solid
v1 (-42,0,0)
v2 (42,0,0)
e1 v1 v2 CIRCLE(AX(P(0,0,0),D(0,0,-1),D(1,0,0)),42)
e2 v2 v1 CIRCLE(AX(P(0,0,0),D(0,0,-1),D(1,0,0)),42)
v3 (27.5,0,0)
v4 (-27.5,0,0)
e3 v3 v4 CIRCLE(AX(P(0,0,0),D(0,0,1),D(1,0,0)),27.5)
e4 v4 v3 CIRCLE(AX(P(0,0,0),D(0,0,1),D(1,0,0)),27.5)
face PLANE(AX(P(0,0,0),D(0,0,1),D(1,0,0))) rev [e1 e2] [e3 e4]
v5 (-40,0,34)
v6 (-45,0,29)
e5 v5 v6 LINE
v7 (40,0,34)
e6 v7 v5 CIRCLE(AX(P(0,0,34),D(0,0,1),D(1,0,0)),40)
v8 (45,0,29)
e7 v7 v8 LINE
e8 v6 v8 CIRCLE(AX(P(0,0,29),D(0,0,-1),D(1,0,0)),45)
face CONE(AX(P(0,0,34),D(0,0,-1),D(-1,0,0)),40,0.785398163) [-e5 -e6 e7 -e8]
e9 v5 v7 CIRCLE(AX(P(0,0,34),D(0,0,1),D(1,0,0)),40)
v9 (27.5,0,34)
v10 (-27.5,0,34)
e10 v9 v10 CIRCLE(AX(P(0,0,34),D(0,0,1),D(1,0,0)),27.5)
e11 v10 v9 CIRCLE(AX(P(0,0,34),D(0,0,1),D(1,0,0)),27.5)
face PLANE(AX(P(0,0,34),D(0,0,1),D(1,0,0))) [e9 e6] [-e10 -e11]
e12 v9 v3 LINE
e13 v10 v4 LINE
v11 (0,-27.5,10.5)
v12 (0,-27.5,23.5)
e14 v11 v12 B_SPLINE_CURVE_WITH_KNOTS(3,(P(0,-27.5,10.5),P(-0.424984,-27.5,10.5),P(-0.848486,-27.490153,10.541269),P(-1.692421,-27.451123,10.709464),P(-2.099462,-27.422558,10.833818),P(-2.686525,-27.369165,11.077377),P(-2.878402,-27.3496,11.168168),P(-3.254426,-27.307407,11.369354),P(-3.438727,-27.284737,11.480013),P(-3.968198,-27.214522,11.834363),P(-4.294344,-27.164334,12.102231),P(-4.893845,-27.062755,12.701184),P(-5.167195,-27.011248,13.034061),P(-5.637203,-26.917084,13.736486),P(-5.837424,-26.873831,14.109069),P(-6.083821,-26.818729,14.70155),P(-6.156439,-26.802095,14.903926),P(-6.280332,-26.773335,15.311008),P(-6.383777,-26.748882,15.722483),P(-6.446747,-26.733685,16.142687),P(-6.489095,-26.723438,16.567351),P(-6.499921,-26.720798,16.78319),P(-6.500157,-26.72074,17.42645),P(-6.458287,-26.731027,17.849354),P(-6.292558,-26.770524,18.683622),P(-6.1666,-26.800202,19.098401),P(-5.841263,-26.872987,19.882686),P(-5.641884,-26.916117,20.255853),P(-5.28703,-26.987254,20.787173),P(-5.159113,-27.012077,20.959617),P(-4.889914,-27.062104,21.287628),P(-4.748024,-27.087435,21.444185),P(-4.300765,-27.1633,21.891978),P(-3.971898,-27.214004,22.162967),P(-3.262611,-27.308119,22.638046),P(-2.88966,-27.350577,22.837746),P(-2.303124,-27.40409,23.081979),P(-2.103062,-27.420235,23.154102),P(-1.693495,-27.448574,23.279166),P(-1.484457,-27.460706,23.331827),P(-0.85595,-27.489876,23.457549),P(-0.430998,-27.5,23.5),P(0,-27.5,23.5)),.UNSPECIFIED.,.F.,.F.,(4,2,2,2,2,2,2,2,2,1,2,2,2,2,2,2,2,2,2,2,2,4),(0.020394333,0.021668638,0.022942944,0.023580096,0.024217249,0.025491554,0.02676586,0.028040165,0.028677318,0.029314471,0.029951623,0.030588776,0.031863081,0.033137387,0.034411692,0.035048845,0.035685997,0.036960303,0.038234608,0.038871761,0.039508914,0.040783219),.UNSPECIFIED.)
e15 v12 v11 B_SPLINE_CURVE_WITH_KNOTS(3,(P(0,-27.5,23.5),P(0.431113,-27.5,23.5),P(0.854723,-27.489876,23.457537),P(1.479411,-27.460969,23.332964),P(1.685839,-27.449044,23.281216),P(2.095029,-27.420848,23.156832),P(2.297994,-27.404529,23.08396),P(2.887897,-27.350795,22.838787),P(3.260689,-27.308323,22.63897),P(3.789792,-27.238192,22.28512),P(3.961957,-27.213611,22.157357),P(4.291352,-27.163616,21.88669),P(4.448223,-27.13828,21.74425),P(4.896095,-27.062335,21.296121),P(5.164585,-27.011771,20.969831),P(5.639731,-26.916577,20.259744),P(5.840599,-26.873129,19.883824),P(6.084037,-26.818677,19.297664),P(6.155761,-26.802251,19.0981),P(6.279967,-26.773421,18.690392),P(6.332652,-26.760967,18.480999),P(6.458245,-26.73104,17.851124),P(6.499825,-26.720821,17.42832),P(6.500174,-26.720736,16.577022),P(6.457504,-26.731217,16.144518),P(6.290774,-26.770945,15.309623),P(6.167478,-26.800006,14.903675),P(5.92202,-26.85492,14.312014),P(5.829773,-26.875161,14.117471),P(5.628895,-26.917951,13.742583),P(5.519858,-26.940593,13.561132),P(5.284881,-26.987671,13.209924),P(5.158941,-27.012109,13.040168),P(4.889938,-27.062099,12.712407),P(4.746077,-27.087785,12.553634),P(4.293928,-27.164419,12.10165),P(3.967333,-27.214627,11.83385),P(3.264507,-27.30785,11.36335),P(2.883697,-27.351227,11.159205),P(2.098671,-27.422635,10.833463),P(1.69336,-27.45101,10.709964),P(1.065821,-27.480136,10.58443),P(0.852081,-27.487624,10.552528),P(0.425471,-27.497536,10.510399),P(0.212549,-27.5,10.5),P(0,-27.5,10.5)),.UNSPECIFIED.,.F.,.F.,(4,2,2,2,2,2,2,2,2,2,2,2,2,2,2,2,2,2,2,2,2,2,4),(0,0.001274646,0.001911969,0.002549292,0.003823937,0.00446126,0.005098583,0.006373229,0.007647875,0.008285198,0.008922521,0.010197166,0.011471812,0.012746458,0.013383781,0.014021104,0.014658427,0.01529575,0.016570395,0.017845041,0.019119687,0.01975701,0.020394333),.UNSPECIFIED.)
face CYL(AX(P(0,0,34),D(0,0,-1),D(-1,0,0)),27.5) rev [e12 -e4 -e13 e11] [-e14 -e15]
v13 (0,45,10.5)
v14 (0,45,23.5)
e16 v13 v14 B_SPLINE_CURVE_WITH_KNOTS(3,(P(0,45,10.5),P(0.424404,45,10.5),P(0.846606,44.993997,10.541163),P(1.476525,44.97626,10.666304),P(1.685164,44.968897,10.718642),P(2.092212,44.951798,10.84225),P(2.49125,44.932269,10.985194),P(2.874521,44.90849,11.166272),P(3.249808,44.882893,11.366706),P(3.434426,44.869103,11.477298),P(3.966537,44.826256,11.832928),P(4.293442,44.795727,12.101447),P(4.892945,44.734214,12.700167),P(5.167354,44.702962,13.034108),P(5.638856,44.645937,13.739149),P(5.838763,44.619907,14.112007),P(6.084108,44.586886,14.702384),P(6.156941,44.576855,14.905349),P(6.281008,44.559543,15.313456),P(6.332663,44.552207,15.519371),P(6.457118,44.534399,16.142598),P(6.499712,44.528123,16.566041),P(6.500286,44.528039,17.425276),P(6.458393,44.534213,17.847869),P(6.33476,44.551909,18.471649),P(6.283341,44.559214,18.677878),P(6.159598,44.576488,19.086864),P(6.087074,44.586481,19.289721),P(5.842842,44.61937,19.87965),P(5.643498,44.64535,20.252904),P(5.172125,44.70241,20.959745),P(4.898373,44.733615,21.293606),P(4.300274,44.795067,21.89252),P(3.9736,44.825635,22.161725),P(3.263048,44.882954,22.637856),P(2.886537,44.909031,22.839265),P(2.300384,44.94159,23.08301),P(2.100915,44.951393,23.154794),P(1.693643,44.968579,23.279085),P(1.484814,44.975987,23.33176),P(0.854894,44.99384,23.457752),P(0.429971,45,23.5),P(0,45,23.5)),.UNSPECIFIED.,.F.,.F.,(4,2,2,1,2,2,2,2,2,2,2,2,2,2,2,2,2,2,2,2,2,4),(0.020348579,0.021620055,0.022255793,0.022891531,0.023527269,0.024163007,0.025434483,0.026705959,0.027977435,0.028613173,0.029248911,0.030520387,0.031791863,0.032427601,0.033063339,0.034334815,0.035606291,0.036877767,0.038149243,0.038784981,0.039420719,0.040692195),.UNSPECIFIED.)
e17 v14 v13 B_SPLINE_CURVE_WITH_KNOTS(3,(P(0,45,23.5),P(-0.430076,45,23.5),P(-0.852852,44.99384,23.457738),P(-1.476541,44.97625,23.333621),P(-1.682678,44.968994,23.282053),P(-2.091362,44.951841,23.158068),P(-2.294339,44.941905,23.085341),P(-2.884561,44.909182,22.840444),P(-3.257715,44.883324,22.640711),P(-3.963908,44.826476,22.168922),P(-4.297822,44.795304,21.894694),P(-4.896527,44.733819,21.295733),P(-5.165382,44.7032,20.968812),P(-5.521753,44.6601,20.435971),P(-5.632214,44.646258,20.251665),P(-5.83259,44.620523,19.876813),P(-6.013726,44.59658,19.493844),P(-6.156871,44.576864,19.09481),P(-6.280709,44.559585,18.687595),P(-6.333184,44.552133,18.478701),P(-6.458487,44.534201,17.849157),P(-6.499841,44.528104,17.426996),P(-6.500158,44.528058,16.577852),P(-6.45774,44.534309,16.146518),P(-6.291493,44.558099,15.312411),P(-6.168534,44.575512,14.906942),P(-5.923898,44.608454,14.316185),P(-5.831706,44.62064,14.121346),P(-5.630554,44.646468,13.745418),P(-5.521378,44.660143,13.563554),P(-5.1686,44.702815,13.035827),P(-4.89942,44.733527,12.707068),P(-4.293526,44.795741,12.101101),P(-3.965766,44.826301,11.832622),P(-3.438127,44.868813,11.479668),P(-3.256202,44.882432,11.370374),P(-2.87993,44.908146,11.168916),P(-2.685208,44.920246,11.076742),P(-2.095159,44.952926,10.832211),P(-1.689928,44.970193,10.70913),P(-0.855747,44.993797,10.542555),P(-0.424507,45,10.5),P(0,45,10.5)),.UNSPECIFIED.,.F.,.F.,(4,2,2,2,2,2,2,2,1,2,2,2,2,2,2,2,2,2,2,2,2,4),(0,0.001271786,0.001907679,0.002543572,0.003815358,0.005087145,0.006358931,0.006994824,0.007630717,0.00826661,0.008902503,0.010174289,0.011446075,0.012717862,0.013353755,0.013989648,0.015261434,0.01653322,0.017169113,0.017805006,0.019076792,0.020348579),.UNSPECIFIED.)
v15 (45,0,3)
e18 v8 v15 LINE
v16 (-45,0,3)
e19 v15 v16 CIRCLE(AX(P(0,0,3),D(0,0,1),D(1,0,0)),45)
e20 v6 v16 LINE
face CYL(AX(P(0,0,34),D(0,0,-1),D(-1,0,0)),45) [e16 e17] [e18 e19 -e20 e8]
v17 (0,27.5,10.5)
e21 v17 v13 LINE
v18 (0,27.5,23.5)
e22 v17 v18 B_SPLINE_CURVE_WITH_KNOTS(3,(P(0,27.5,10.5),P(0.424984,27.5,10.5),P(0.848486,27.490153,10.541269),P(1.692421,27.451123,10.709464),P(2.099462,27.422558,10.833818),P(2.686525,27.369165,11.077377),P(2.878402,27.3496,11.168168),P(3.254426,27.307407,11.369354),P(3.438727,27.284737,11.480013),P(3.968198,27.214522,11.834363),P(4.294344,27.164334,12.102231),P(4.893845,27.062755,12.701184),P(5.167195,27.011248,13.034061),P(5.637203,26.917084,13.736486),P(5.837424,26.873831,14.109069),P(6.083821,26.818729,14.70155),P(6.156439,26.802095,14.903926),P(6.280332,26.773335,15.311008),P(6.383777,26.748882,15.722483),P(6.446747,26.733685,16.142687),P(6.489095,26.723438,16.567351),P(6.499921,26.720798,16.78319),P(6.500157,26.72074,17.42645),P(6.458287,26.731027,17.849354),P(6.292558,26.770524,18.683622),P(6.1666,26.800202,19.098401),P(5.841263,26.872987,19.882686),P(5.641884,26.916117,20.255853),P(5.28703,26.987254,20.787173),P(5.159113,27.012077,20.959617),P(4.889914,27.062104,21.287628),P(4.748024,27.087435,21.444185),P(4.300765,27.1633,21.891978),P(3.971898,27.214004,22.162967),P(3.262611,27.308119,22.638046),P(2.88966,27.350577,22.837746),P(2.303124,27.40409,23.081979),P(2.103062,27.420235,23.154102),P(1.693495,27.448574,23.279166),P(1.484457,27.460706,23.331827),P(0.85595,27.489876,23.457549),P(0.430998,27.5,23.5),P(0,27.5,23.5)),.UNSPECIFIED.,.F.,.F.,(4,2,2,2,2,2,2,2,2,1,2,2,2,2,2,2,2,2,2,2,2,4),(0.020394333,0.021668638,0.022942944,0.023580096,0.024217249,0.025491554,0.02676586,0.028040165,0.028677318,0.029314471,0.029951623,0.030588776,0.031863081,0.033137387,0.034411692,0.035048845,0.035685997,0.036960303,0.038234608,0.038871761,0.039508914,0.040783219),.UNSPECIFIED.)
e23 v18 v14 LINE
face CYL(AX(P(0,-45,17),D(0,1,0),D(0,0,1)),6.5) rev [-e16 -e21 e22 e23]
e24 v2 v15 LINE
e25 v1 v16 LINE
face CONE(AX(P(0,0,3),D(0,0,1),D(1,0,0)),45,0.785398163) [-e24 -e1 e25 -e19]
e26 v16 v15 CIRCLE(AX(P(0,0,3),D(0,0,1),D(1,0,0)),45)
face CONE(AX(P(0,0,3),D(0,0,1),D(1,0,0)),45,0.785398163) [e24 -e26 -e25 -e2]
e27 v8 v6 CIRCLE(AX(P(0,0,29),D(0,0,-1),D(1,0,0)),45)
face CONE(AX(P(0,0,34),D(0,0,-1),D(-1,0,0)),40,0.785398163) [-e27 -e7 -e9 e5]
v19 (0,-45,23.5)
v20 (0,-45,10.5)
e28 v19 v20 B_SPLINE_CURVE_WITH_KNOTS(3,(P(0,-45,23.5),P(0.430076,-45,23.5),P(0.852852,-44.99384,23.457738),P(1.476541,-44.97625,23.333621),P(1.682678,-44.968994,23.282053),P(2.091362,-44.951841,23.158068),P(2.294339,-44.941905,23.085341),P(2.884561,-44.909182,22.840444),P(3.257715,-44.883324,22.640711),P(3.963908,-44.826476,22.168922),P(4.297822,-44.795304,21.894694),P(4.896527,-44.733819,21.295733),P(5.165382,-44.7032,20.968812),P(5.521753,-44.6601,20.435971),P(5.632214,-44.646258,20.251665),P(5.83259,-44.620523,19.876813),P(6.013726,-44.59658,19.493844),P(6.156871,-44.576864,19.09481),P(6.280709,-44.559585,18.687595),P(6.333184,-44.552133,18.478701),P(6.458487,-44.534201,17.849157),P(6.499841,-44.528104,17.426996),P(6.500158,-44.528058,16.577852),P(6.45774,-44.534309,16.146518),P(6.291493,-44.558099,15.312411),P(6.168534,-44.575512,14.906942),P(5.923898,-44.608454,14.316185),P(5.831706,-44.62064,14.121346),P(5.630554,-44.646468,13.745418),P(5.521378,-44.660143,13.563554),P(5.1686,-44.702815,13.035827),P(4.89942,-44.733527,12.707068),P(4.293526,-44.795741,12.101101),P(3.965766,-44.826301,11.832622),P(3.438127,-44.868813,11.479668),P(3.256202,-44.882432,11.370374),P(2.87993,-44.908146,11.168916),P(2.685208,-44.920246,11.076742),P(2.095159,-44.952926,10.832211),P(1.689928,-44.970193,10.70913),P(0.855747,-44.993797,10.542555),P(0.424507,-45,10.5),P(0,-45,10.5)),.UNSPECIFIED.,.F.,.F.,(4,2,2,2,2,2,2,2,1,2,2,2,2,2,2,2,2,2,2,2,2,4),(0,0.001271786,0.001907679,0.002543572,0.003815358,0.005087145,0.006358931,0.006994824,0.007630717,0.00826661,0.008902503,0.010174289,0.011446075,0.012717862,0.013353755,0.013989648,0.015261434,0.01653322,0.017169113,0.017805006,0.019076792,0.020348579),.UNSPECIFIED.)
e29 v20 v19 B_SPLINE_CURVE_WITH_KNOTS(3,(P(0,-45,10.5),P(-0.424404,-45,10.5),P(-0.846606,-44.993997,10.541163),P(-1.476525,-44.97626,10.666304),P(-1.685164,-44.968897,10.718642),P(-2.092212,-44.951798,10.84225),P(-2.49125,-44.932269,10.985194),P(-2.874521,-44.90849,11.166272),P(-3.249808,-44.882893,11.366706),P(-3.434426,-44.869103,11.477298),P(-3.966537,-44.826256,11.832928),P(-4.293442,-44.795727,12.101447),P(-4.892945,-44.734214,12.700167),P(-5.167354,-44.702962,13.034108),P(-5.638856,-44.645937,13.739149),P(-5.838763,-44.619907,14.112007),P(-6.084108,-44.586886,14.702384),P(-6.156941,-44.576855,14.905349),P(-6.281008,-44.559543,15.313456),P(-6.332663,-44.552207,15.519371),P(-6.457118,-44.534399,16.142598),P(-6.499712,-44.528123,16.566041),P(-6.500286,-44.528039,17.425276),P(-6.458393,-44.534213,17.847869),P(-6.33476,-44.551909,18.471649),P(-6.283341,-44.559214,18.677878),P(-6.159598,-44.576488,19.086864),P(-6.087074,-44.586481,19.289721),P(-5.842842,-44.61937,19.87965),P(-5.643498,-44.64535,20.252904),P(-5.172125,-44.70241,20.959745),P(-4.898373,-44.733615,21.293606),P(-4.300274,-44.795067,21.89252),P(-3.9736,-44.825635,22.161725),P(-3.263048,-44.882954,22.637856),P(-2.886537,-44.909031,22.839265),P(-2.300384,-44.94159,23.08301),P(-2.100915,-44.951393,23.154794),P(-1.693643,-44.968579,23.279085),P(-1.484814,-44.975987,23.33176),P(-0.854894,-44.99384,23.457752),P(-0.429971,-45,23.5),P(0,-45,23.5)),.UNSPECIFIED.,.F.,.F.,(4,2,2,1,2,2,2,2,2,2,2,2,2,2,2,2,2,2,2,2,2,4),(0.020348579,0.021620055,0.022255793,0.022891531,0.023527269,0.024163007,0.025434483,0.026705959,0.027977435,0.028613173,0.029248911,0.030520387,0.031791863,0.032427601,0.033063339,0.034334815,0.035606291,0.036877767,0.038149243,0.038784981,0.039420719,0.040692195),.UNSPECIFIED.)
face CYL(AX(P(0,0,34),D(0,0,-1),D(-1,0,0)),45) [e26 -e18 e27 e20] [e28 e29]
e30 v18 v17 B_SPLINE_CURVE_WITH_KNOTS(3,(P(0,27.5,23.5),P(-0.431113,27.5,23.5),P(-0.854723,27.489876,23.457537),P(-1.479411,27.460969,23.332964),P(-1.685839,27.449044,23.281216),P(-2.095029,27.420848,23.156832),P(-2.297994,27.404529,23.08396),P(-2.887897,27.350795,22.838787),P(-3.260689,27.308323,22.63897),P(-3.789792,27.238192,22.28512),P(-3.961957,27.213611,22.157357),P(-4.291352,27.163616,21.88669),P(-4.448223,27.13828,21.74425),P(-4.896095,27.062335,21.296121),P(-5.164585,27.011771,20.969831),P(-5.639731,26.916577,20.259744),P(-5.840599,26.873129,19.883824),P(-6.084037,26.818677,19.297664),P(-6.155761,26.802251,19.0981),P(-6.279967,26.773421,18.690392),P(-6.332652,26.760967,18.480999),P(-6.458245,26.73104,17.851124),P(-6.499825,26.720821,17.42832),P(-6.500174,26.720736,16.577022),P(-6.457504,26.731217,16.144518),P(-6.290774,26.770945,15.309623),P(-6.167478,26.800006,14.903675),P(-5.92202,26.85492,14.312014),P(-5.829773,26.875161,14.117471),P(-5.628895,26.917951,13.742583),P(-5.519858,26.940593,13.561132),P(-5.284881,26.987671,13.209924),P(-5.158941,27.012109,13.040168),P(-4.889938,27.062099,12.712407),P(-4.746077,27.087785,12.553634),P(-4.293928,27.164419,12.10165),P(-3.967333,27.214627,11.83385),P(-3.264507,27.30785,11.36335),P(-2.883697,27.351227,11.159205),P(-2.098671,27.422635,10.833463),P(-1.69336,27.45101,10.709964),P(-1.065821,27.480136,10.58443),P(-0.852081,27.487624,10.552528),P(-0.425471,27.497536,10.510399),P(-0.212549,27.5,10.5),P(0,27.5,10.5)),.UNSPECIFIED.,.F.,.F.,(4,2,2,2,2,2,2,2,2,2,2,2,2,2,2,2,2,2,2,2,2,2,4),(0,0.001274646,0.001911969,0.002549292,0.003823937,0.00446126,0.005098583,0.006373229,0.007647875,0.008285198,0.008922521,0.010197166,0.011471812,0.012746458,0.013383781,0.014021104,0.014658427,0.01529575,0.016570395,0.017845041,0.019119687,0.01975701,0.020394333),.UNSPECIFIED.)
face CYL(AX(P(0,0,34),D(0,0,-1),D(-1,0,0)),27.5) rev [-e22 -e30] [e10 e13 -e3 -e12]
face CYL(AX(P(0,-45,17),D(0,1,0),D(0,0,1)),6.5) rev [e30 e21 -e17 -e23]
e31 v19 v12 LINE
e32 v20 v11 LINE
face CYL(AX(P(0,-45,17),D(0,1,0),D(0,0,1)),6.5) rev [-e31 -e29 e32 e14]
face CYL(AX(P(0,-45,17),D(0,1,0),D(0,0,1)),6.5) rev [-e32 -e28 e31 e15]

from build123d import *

# Parameters (mm, degrees)
SKETCH1_R               = 45
SKETCH1_R_2             = 27.5
BOSS_EXTRUDE1_DEPTH     = 34
CUT_EXTRUDE1_DEPTH      = 73.15261603
CUT_EXTRUDE1_DEPTH_BACK = 73.15261603
SKETCH3_R               = 6.5
CHAMFER1_SIZE           = 5
CHAMFER2_SIZE           = 3


with BuildPart() as part:
    # Sketch1 → Boss-Extrude1 (new body)
    with BuildSketch(Plane.XY):
        Circle(SKETCH1_R)
        Circle(SKETCH1_R_2, mode=Mode.SUBTRACT)
    extrude(amount=BOSS_EXTRUDE1_DEPTH)

    # Sketch3 → Cut-Extrude1 (cut, two sides: drawn at the far end of the back side and taken through both)
    with BuildSketch(Plane(origin=(0, 0, 0), x_dir=(1, 0, 0), z_dir=(0, 1, 0)).offset(-CUT_EXTRUDE1_DEPTH_BACK)):
        with Locations(Location((0, -17, 0), (0, 0, 270))):
            Circle(SKETCH3_R)
    extrude(amount=CUT_EXTRUDE1_DEPTH + CUT_EXTRUDE1_DEPTH_BACK, mode=Mode.SUBTRACT)

    # Chamfer1
    chamfer1_edges = [part.edges().sort_by_distance(p)[0] for p in [
        (-45, 0, 34),
    ]]
    chamfer(chamfer1_edges, length=CHAMFER1_SIZE)

    # Chamfer2
    chamfer2_edges = [part.edges().sort_by_distance(p)[0] for p in [
        (-45, 0, 0),
    ]]
    chamfer(chamfer2_edges, length=CHAMFER2_SIZE)


solid = part.part
